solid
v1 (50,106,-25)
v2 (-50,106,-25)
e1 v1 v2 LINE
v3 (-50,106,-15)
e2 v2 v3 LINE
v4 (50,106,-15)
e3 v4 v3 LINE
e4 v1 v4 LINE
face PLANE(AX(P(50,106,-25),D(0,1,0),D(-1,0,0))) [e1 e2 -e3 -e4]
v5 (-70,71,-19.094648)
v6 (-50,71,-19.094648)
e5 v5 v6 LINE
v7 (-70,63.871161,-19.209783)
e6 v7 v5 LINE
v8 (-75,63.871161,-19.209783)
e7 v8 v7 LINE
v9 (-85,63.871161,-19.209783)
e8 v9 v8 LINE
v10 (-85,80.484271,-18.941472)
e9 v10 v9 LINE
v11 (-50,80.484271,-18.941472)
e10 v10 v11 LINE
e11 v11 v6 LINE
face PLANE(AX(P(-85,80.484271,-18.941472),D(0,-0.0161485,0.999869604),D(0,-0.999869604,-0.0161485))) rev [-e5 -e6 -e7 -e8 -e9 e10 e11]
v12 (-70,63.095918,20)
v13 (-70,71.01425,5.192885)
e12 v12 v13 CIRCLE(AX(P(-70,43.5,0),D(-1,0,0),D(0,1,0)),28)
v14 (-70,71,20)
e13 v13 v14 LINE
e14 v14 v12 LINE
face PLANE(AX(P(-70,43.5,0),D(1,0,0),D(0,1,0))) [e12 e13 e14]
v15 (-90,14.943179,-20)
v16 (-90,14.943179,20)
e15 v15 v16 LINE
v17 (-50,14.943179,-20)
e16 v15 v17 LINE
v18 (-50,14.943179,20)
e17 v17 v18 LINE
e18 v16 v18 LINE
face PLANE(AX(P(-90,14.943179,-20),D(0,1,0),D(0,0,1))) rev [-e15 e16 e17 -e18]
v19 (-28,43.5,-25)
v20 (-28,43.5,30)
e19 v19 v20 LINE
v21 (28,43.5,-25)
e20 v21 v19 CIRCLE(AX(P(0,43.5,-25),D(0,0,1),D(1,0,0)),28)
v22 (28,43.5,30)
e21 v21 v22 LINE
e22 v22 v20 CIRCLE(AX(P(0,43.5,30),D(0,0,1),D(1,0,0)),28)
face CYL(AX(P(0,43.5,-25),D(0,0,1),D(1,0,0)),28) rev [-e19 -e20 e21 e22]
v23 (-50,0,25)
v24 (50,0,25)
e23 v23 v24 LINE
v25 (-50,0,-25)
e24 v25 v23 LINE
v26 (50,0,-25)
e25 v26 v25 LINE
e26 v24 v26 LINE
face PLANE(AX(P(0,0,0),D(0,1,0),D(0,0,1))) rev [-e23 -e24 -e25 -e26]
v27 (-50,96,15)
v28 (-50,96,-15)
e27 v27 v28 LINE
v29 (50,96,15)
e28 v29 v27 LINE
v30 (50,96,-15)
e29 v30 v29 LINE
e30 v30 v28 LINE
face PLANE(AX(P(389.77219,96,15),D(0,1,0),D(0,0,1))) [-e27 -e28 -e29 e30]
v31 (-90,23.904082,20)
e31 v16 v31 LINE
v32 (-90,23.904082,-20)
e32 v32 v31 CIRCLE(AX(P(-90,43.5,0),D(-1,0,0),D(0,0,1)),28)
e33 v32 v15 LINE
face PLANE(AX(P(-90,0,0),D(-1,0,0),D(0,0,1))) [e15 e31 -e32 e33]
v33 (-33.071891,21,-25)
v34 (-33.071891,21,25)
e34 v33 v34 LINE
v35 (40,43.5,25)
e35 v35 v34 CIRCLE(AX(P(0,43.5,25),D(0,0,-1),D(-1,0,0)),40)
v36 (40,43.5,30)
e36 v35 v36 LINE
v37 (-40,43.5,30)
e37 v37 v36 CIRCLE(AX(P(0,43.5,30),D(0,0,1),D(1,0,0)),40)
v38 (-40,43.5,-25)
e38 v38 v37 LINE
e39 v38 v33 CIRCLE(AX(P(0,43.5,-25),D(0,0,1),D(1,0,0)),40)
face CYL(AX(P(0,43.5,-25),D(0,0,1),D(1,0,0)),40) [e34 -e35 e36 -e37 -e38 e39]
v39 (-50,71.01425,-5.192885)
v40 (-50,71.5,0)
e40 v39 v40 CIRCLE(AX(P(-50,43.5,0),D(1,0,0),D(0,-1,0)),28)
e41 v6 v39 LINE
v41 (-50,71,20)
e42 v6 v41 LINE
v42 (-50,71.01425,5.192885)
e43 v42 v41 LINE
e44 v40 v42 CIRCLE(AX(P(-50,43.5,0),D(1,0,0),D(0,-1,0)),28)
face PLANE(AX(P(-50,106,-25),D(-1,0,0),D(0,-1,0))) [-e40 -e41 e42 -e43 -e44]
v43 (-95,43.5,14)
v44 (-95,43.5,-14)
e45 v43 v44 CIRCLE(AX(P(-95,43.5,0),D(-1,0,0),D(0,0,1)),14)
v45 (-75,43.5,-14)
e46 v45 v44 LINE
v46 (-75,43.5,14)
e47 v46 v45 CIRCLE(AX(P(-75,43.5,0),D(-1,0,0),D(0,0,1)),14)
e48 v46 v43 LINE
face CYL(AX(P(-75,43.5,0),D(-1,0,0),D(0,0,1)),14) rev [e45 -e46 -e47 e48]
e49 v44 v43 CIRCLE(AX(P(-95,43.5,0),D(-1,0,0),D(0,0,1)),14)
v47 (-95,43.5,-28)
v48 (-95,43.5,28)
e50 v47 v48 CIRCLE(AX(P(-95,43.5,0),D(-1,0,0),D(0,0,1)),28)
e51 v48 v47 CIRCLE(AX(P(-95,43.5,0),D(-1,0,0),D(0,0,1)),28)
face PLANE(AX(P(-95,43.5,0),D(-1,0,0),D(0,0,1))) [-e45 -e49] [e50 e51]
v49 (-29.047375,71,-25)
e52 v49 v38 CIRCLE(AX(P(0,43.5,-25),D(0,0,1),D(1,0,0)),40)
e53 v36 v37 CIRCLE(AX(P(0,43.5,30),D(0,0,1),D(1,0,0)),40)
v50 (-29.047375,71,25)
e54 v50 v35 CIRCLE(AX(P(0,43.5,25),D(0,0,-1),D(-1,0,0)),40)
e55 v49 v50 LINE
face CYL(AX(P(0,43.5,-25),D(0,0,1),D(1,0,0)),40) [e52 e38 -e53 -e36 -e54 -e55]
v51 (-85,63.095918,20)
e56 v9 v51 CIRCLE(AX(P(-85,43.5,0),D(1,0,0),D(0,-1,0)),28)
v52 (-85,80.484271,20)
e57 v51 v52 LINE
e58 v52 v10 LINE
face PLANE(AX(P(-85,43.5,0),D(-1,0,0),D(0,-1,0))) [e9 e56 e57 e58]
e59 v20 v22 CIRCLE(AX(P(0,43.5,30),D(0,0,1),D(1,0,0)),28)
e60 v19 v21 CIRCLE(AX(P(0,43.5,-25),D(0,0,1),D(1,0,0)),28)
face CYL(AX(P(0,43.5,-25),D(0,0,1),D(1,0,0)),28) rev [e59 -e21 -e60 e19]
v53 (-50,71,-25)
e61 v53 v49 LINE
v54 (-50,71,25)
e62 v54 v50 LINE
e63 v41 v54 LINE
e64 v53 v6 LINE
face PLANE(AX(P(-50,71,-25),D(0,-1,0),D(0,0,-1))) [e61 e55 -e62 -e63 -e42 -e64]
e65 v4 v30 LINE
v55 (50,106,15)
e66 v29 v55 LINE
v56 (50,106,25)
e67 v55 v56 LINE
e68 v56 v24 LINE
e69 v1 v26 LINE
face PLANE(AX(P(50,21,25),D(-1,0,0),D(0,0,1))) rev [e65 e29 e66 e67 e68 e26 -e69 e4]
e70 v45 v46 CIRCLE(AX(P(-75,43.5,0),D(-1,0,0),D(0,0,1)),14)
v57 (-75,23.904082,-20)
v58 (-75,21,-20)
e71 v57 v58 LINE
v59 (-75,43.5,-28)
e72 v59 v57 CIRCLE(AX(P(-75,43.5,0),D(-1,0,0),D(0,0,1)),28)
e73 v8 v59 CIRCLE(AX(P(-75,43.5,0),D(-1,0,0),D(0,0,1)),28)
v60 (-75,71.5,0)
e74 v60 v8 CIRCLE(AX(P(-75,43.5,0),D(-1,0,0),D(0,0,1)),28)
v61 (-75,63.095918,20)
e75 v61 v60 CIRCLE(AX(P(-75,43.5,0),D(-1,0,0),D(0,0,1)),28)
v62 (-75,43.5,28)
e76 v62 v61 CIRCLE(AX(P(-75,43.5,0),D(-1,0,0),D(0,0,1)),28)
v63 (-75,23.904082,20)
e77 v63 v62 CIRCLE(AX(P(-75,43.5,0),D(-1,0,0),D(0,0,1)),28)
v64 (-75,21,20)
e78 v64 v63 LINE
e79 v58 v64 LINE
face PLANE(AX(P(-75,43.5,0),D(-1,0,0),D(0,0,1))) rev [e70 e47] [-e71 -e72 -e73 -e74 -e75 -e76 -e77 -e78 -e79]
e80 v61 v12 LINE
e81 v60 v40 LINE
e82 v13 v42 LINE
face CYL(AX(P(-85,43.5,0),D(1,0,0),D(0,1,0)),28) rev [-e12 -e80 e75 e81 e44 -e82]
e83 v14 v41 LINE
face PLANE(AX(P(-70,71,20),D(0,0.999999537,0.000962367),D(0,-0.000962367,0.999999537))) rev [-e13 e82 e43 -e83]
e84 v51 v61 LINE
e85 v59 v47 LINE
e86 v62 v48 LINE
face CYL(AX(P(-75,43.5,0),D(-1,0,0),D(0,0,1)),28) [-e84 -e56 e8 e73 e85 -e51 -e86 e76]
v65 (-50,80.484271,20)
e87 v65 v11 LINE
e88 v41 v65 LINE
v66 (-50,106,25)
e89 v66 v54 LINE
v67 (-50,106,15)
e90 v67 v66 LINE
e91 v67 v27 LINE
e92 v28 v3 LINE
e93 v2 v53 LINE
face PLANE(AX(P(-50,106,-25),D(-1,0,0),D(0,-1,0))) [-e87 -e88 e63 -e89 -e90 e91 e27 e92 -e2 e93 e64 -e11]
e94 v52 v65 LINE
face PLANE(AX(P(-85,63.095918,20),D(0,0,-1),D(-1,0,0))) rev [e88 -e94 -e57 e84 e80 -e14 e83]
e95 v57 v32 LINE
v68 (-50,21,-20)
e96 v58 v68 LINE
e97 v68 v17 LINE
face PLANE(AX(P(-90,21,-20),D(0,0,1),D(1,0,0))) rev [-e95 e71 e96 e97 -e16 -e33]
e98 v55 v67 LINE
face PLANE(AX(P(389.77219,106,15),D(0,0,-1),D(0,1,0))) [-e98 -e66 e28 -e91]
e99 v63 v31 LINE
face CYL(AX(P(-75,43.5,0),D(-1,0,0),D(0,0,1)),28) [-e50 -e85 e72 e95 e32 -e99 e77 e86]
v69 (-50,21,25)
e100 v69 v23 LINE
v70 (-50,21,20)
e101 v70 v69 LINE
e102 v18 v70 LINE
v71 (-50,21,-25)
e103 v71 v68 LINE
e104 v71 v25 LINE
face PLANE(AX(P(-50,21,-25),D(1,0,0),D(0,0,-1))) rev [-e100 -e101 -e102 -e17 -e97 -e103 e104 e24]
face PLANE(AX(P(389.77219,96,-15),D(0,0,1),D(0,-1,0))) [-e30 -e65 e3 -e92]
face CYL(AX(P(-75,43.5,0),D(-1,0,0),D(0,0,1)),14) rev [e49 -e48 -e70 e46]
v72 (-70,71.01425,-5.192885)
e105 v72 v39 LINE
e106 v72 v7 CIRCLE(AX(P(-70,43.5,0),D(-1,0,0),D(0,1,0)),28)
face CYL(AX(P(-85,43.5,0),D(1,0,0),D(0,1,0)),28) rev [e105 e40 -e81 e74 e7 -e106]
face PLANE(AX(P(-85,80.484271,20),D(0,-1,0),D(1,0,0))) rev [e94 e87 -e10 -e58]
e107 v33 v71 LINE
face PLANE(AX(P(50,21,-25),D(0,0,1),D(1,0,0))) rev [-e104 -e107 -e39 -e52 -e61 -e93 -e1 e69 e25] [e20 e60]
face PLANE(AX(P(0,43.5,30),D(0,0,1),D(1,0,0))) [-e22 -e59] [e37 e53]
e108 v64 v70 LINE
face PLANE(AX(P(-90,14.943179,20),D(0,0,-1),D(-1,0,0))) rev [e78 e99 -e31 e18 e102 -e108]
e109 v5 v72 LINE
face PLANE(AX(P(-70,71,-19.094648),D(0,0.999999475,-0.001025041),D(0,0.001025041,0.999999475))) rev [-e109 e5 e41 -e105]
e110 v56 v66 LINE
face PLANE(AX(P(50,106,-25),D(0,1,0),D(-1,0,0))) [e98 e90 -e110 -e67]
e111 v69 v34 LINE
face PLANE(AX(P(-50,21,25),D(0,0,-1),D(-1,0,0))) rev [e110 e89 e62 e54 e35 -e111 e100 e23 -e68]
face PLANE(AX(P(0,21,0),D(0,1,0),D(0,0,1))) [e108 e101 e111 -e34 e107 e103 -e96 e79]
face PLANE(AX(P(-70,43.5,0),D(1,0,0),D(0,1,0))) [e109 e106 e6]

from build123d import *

# Parameters (mm, degrees)
BASE_PLATE_SKETCH_W        = 100
BASE_PLATE_SKETCH_H        = 50
BASE_PLATE_DEPTH           = 21
SIDE_WEB_SKETCH_W          = 40
SIDE_WEB_SKETCH_H          = 6.056820609
SIDE_WEB_DEPTH             = 40
REAR_BORE_BOSS_DEPTH       = 5
REAR_BORE_BOSS_DEPTH_BACK  = 15
REAR_BORE_BOSS_SKETCH_R    = 28
REAR_BORE_BOSS_SKETCH_R_2  = 14
FRONT_BORE_BOSS_DEPTH      = 5
FRONT_BORE_BOSS_DEPTH_BACK = 50
FRONT_BORE_BOSS_SKETCH_R   = 40
FRONT_BORE_BOSS_SKETCH_R_2 = 28
FRONT_BORE_REACH           = 141.145
FRONT_BORE_SKETCH_R        = 28
UPRIGHT_WALL_DEPTH         = 50
TOP_SLOT_10X10_DEPTH       = 183.101619982
TOP_SLOT_10X10_DEPTH_BACK  = 132
REAR_START                 = 35
REAR_BLOCK_DEPTH           = 35
REAR_START_2               = -20
REAR_BORE_CUT_DEPTH        = 20
REAR_LUG_DEPTH             = 15


with BuildPart() as part:
    # Base Plate Sketch → Base Plate (new body)
    with BuildSketch(Plane(origin=(0, 0, 0), x_dir=(1, 0, 0), z_dir=(0, 1, 0))):
        Rectangle(BASE_PLATE_SKETCH_W, BASE_PLATE_SKETCH_H)
    extrude(amount=BASE_PLATE_DEPTH)

    # Side Web Sketch → Side Web (add)
    with BuildSketch(Plane.ZY.offset(50)):
        with Locations((0, 17.971589696)):
            Rectangle(SIDE_WEB_SKETCH_W, SIDE_WEB_SKETCH_H)
    extrude(amount=SIDE_WEB_DEPTH)

    # Rear Bore Boss Sketch → Rear Bore Boss (add, two sides: drawn at the far end of the back side and taken through both)
    with BuildSketch(Plane.ZY.offset(90).offset(-REAR_BORE_BOSS_DEPTH_BACK)):
        with Locations((0, 43.5)):
            Circle(REAR_BORE_BOSS_SKETCH_R)
        with Locations((0, 43.5)):
            Circle(REAR_BORE_BOSS_SKETCH_R_2, mode=Mode.SUBTRACT)
    extrude(amount=REAR_BORE_BOSS_DEPTH + REAR_BORE_BOSS_DEPTH_BACK)

    # Front Bore Boss Sketch → Front Bore Boss (add, two sides: drawn at the far end of the back side and taken through both)
    with BuildSketch(Plane.XY.offset(25).offset(-FRONT_BORE_BOSS_DEPTH_BACK)):
        with Locations((0, 43.5)):
            Circle(FRONT_BORE_BOSS_SKETCH_R)
        with Locations((0, 43.5)):
            Circle(FRONT_BORE_BOSS_SKETCH_R_2, mode=Mode.SUBTRACT)
    extrude(amount=FRONT_BORE_BOSS_DEPTH + FRONT_BORE_BOSS_DEPTH_BACK)

    # Front Bore Sketch → Front Bore (cut, up to next)
    with BuildSketch(Plane.XY.offset(30), mode=Mode.PRIVATE) as front_bore_sk1:
        with Locations((0, 43.5)):
            Circle(FRONT_BORE_SKETCH_R)
    front_bore_tool1 = extrude(front_bore_sk1.sketch, amount=-FRONT_BORE_REACH, mode=Mode.PRIVATE) & part.part
    add(front_bore_tool1.solids().sort_by_distance((0, 43.5, 30))[0], mode=Mode.SUBTRACT)

    # Upright Wall Sketch → Upright Wall (add)
    with BuildSketch(Plane.XY.offset(25)):
        with BuildLine():
            Line((50, 21), (50, 106))
            Line((50, 106), (-50, 106))
            Line((-50, 106), (-50, 71))
            Line((-50, 71), (-29.047375097, 71))
            ThreePointArc((-29.047375097, 71), (25.080852913, 74.660083715), (33.071891388, 21))
            Line((33.071891388, 21), (50, 21))
        make_face()
    extrude(amount=-UPRIGHT_WALL_DEPTH)

    # Top Slot Sketch → Top Slot 10x10 (cut, two sides: drawn at the far end of the back side and taken through both)
    with BuildSketch(Plane(origin=(50, 0, 0), x_dir=(0, 0, -1), z_dir=(1, 0, 0)).offset(-TOP_SLOT_10X10_DEPTH_BACK)):
        Polygon((-15, 346.312830732), (-15, 106), (-15, 96), (15, 96), (15, 106), (15, 346.312830732), (15, 826.938492197), (-15, 826.938492197), align=None)
    extrude(amount=TOP_SLOT_10X10_DEPTH + TOP_SLOT_10X10_DEPTH_BACK, mode=Mode.SUBTRACT)

    # Rear Block Sketch → Rear Block (add)
    with BuildSketch(Plane.ZY.offset(50).offset(REAR_START)):
        with BuildLine():
            Line((-18.941471656, 80.4842707), (-19.209783437, 63.871161486))
            ThreePointArc((-19.209783437, 63.871161486), (0.553499044, 71.49452873), (20, 63.095917942))
            Line((20, 63.095917942), (20, 80.4842707))
            Line((20, 80.4842707), (-18.941471656, 80.4842707))
        make_face()
    extrude(amount=-REAR_BLOCK_DEPTH)

    # Rear Bore Cut Sketch → Rear Bore Cut (cut)
    with BuildSketch(Plane(origin=(-50, 0, 0), x_dir=(0, 0, -1), z_dir=(1, 0, 0)).offset(REAR_START_2)):
        with BuildLine():
            Line((-20, 71), (-20, 63.095917942))
            ThreePointArc((-20, 63.095917942), (-13.203990192, 68.191185532), (-5.192884853, 71.014249888))
            Line((-5.192884853, 71.014249888), (-20, 71))
        make_face()
        with BuildLine():
            Line((19.209783437, 63.871161486), (19.094648375, 71))
            Line((19.094648375, 71), (5.192884853, 71.014249888))
            ThreePointArc((5.192884853, 71.014249888), (12.713319114, 68.447374954), (19.209783437, 63.871161486))
        make_face()
    extrude(amount=REAR_BORE_CUT_DEPTH, mode=Mode.SUBTRACT)

    # Rear Lug Sketch → Rear Lug (add)
    with BuildSketch(Plane.ZY.offset(90)):
        with BuildLine():
            Line((-20, 14.943179391), (-20, 23.904082058))
            ThreePointArc((-20, 23.904082058), (0, 15.5), (20, 23.904082058))
            Line((20, 23.904082058), (20, 14.943179391))
            Line((20, 14.943179391), (-20, 14.943179391))
        make_face()
    extrude(amount=-REAR_LUG_DEPTH)


solid = part.part
